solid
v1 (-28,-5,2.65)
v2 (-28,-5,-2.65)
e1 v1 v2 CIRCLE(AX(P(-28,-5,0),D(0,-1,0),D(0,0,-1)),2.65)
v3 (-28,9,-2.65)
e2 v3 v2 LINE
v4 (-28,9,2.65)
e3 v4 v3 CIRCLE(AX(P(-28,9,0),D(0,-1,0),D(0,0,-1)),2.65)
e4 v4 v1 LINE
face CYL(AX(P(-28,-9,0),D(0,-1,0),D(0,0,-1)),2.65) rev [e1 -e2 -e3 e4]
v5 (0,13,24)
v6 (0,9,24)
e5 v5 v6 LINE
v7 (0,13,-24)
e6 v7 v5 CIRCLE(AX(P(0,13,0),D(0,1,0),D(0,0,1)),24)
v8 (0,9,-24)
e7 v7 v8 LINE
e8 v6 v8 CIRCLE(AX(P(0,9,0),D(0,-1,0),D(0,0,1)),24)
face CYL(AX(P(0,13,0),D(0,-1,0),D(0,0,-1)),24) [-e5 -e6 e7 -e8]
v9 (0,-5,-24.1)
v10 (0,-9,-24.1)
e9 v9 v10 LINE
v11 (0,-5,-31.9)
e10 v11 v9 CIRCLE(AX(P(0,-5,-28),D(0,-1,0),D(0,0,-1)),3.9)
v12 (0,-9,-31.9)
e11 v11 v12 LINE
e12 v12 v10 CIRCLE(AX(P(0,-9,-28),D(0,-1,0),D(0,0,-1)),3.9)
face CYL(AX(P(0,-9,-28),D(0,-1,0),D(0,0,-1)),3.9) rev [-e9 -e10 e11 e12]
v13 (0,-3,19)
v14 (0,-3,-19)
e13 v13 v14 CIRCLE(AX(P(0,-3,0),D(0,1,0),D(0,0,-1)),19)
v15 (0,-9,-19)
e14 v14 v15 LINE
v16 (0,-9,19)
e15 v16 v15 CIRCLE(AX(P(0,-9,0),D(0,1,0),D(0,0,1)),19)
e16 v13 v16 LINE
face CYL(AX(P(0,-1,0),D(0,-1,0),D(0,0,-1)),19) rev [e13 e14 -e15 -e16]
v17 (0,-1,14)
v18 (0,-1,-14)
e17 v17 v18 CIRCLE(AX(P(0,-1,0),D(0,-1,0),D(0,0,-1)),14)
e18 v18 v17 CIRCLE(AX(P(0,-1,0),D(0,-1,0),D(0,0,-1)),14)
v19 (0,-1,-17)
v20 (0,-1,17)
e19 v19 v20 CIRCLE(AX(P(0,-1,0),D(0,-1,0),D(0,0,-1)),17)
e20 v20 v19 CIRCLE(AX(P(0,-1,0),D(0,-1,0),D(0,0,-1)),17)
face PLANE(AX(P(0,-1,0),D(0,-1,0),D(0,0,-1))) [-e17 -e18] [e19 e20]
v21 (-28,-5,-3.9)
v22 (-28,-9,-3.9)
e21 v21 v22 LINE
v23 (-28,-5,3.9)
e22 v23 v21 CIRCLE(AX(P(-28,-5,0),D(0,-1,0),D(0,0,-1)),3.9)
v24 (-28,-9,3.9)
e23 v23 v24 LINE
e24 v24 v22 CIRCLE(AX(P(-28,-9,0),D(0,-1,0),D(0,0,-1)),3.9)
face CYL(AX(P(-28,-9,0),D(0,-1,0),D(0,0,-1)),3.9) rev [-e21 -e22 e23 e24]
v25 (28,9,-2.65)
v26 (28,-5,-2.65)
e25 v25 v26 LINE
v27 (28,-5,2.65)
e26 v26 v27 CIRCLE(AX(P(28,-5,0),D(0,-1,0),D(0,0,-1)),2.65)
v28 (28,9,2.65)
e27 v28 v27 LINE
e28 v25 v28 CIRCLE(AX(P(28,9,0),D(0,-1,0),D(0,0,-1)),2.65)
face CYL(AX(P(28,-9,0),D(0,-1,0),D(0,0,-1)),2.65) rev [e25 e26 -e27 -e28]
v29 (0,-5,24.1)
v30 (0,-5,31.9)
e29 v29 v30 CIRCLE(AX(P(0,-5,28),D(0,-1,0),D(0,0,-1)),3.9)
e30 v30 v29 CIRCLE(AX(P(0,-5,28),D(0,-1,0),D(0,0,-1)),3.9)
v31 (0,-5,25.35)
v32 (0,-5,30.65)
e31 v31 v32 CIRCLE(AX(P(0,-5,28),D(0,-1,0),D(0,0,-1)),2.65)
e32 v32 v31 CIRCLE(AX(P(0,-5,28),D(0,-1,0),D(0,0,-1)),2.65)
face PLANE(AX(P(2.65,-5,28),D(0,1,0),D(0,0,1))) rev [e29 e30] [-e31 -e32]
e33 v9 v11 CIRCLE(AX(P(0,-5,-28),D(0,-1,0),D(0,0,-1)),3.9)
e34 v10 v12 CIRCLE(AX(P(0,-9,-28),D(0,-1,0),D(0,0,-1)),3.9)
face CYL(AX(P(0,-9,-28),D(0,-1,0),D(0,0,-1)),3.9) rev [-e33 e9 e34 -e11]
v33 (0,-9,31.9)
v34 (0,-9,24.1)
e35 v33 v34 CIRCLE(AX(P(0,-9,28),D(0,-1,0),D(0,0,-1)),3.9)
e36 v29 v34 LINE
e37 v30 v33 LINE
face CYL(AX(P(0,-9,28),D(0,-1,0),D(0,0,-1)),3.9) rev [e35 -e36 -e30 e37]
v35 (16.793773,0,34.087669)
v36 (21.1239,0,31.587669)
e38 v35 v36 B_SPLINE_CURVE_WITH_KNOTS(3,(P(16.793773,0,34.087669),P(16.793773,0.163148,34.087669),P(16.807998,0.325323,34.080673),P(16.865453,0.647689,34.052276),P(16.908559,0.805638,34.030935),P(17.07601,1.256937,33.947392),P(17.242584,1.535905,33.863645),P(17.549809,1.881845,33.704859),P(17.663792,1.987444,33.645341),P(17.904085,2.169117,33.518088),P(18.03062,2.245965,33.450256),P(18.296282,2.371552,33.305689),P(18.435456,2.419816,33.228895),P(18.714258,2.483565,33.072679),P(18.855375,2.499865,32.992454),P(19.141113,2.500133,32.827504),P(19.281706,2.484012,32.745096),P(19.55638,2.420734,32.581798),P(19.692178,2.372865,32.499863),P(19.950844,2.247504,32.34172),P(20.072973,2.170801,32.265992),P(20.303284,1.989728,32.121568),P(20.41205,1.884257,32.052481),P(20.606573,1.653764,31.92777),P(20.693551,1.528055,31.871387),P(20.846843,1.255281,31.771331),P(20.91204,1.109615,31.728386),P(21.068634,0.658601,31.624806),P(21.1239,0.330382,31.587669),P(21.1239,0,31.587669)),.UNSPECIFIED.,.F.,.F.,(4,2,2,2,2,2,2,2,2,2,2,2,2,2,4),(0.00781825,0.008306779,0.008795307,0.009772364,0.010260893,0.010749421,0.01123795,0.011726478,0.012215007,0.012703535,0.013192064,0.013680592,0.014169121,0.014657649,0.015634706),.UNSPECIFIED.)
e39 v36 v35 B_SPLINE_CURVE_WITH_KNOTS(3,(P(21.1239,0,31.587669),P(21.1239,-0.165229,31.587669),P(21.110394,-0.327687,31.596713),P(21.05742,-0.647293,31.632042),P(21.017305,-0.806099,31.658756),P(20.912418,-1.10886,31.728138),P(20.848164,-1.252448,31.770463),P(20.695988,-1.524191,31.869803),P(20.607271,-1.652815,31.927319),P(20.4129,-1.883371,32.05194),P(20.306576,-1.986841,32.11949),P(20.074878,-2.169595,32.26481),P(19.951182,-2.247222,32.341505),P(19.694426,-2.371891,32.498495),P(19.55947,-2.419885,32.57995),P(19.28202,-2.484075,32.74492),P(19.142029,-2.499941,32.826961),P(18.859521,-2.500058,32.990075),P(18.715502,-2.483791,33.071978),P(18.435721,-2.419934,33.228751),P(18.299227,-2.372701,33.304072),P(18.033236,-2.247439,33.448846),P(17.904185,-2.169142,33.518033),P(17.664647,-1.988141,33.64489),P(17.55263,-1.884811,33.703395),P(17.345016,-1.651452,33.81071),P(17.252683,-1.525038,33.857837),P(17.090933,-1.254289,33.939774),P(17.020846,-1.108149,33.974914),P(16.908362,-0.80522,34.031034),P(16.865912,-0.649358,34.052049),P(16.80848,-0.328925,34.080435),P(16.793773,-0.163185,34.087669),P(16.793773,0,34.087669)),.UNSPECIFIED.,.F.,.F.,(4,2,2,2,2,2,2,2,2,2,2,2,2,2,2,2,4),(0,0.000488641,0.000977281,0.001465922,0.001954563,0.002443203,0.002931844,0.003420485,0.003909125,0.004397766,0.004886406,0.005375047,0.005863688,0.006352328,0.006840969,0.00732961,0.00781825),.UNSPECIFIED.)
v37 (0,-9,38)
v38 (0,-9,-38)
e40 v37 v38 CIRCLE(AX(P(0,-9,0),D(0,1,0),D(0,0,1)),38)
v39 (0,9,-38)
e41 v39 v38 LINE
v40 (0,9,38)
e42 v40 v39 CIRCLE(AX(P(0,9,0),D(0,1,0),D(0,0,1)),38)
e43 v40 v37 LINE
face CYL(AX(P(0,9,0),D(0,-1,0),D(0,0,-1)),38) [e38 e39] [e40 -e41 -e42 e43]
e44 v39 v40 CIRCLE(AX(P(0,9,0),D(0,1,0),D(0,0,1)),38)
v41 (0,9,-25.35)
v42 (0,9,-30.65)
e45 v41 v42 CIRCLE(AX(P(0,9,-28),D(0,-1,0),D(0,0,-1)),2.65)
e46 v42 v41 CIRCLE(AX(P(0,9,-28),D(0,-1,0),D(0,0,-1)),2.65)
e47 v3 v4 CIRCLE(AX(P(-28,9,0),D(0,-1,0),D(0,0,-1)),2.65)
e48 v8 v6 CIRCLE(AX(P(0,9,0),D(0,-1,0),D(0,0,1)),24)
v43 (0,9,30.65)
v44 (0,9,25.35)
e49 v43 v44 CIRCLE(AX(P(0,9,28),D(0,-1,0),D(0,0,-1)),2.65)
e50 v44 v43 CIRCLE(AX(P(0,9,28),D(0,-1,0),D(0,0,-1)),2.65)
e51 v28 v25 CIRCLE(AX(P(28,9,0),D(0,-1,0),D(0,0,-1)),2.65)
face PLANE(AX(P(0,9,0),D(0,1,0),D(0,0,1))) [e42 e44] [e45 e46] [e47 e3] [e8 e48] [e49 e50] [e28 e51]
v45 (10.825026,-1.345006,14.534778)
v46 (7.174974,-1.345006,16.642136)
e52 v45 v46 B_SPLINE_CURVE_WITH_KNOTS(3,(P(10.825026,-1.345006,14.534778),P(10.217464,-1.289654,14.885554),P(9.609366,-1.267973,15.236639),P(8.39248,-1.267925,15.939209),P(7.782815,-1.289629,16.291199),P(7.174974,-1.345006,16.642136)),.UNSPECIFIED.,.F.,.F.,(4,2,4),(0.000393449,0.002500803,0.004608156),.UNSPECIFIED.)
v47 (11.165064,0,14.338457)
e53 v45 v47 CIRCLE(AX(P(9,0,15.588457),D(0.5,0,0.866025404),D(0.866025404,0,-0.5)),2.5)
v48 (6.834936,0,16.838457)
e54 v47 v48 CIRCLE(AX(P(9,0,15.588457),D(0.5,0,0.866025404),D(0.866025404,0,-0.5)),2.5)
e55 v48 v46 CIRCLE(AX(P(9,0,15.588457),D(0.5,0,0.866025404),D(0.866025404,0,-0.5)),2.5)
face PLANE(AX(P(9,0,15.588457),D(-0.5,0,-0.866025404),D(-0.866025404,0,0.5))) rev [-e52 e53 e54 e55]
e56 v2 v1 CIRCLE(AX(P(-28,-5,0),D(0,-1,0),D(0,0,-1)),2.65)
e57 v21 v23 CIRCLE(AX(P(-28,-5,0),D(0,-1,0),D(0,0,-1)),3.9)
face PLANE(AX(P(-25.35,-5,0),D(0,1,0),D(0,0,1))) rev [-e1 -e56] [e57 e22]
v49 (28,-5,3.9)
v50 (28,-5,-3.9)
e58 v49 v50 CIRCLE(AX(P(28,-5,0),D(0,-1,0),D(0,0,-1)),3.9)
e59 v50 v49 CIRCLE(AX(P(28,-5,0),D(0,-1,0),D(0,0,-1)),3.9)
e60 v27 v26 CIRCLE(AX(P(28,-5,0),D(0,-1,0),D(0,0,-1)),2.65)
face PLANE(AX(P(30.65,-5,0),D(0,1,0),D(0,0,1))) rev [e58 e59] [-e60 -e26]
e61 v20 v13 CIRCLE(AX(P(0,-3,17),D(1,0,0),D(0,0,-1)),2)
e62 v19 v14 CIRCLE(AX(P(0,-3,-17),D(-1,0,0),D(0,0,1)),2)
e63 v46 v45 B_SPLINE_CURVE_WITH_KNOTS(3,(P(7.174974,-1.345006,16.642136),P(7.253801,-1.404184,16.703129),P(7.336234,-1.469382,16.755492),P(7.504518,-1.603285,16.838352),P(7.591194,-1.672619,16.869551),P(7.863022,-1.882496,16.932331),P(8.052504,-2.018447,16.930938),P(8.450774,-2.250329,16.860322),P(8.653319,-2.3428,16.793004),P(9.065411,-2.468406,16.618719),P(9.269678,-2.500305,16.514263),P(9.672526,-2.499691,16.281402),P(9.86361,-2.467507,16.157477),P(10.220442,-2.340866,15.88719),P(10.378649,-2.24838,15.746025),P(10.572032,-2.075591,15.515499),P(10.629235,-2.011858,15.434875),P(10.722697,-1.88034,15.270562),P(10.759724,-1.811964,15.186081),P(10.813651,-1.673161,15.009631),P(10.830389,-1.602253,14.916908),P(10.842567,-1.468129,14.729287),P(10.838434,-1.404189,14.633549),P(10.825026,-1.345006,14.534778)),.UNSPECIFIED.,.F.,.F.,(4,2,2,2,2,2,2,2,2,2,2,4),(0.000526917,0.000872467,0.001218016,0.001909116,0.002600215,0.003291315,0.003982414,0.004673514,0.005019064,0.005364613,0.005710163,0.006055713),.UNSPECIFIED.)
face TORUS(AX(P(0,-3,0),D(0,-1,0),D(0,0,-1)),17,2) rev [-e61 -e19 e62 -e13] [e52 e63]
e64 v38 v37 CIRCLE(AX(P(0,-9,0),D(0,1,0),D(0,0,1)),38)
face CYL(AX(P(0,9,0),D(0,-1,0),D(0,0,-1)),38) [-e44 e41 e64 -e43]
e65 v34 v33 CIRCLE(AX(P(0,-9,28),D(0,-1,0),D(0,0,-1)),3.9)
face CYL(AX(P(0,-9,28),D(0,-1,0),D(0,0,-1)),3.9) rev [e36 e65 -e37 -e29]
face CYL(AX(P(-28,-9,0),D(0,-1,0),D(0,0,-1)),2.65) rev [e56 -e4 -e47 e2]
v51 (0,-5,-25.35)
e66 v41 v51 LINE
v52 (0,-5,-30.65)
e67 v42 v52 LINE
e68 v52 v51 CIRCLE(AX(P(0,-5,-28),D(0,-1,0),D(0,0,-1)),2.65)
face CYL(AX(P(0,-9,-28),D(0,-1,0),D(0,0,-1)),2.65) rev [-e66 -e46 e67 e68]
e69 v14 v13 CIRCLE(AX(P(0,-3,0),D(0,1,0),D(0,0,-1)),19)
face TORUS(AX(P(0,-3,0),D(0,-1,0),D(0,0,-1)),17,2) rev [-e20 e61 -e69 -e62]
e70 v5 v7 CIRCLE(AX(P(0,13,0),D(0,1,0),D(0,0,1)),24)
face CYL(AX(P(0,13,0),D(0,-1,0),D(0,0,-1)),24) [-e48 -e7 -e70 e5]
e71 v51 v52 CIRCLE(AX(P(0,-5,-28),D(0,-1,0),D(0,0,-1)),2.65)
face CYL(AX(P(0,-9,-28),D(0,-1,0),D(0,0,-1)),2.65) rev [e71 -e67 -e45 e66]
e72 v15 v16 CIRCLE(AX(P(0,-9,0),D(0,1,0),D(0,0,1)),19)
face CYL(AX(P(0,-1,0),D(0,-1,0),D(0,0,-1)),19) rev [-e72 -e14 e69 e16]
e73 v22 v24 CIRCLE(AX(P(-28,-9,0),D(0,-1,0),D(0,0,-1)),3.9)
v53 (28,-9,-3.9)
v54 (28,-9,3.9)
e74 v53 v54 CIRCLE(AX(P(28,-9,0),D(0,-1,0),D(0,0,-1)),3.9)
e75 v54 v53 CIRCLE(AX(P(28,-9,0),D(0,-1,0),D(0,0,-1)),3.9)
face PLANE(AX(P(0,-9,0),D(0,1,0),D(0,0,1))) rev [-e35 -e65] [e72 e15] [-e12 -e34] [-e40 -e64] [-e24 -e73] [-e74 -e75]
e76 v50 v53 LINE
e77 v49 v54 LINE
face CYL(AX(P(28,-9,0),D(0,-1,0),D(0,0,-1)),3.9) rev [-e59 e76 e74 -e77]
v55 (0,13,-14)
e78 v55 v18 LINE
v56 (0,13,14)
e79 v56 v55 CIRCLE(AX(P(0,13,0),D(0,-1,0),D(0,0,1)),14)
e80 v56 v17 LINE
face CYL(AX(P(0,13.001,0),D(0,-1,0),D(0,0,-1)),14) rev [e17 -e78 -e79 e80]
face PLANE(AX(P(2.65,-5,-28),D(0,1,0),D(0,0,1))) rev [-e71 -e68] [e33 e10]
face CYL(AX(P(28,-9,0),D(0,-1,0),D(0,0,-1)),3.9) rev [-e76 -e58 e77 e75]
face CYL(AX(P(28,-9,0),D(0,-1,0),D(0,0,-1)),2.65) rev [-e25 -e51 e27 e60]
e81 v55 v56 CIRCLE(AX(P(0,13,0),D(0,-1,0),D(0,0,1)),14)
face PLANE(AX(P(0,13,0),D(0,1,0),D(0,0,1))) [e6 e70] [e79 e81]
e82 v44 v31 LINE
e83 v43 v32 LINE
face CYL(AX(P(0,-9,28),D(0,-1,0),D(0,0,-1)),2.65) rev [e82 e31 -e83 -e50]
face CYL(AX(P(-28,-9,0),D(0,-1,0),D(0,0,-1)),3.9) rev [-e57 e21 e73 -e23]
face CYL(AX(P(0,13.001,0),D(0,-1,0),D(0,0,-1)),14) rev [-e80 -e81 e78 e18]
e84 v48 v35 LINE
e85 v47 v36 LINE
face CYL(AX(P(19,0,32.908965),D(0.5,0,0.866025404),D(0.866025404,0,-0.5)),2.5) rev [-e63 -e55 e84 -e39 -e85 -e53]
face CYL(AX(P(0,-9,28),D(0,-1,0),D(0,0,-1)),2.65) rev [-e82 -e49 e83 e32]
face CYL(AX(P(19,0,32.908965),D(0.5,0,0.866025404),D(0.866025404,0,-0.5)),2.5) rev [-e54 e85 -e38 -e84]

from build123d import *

# Parameters (mm, degrees)
BASE_DISC_SKETCH_R                          = 38
BASE_DISC_76X18_DEPTH                       = 9
SPIGOT_SKETCH_R                             = 24
SPIGOT_48X8_DEPTH                           = 4
COUNTERBORED_MOUNTING_HOLES_5_3_D           = 5.3
COUNTERBORED_MOUNTING_HOLES_5_3_CBORE_D     = 7.8
COUNTERBORED_MOUNTING_HOLES_5_3_CBORE_DEPTH = 4
COUNTERBORE_BORE_SKETCH_R                   = 19
COUNTERBORE_BORE_38X16_DEPTH                = 8
THROUGH_BORE_28_REACH                       = 57.534
THROUGH_BORE_SKETCH_R                       = 14
BORE_EDGE_FILLET_R2_R                       = 2
RADIAL_HOLE_5X20_D                          = 5
RADIAL_HOLE_5X20_DEPTH                      = 20


with BuildPart() as part:
    # Base Disc Sketch → Base Disc Ø76x18 (new, symmetric)
    with BuildSketch(Plane(origin=(0, 0, 0), x_dir=(1, 0, 0), z_dir=(0, 1, 0))):
        with Locations(Location((0, 0, 0), (0, 0, 270))):
            Circle(BASE_DISC_SKETCH_R)
    extrude(amount=BASE_DISC_76X18_DEPTH, both=True)

    # Spigot Sketch → Spigot Ø48x8 (add, symmetric)
    with BuildSketch(Plane(origin=(0, 9, 0), x_dir=(1, 0, 0), z_dir=(0, 1, 0))):
        with Locations(Location((0, 0, 0), (0, 0, 270))):
            Circle(SPIGOT_SKETCH_R)
    extrude(amount=SPIGOT_48X8_DEPTH, both=True)

    # Counterbored Mounting Holes Ø5.3 (through all)
    with Locations(Plane(origin=(0, -9, 28), x_dir=(0, 0, -1), z_dir=(0, -1, 0))):
        with Locations((0, 0), (28, 28), (56, 0), (28, -28)):
            CounterBoreHole(COUNTERBORED_MOUNTING_HOLES_5_3_D / 2, COUNTERBORED_MOUNTING_HOLES_5_3_CBORE_D / 2, COUNTERBORED_MOUNTING_HOLES_5_3_CBORE_DEPTH)

    # Counterbore Bore Sketch → Counterbore Bore Ø38x16 (cut, symmetric)
    with BuildSketch(Plane.XZ.offset(9)):
        with Locations(Location((0, 0, 0), (0, 0, 270))):
            Circle(COUNTERBORE_BORE_SKETCH_R)
    extrude(amount=COUNTERBORE_BORE_38X16_DEPTH, both=True, mode=Mode.SUBTRACT)

    # Through Bore Sketch → Through Bore Ø28 (cut, up to next)
    with BuildSketch(Plane.XZ.offset(1), mode=Mode.PRIVATE) as through_bore_28_sk1:
        with Locations(Location((0, 0, 0), (0, 0, 270))):
            Circle(THROUGH_BORE_SKETCH_R)
    through_bore_28_tool1 = extrude(through_bore_28_sk1.sketch, amount=-THROUGH_BORE_28_REACH, mode=Mode.PRIVATE) & part.part
    add(through_bore_28_tool1.solids().sort_by_distance((0, -1, 0))[0], mode=Mode.SUBTRACT)

    # Bore Edge Fillet R2
    bore_edge_fillet_r2_edges = [part.edges().sort_by_distance(p)[0] for p in [
        (0, -1, 19),
    ]]
    fillet(bore_edge_fillet_r2_edges, radius=BORE_EDGE_FILLET_R2_R)

    # Radial Hole Ø5x20
    with Locations(Plane(origin=(19, 0, 32.908965344), x_dir=(0.8660254037844379, 0, -0.5000000000000013), z_dir=(0.5000000000000013, 0, 0.8660254037844379))):
        with Locations((0, 0)):
            Hole(RADIAL_HOLE_5X20_D / 2, depth=RADIAL_HOLE_5X20_DEPTH)


solid = part.part
